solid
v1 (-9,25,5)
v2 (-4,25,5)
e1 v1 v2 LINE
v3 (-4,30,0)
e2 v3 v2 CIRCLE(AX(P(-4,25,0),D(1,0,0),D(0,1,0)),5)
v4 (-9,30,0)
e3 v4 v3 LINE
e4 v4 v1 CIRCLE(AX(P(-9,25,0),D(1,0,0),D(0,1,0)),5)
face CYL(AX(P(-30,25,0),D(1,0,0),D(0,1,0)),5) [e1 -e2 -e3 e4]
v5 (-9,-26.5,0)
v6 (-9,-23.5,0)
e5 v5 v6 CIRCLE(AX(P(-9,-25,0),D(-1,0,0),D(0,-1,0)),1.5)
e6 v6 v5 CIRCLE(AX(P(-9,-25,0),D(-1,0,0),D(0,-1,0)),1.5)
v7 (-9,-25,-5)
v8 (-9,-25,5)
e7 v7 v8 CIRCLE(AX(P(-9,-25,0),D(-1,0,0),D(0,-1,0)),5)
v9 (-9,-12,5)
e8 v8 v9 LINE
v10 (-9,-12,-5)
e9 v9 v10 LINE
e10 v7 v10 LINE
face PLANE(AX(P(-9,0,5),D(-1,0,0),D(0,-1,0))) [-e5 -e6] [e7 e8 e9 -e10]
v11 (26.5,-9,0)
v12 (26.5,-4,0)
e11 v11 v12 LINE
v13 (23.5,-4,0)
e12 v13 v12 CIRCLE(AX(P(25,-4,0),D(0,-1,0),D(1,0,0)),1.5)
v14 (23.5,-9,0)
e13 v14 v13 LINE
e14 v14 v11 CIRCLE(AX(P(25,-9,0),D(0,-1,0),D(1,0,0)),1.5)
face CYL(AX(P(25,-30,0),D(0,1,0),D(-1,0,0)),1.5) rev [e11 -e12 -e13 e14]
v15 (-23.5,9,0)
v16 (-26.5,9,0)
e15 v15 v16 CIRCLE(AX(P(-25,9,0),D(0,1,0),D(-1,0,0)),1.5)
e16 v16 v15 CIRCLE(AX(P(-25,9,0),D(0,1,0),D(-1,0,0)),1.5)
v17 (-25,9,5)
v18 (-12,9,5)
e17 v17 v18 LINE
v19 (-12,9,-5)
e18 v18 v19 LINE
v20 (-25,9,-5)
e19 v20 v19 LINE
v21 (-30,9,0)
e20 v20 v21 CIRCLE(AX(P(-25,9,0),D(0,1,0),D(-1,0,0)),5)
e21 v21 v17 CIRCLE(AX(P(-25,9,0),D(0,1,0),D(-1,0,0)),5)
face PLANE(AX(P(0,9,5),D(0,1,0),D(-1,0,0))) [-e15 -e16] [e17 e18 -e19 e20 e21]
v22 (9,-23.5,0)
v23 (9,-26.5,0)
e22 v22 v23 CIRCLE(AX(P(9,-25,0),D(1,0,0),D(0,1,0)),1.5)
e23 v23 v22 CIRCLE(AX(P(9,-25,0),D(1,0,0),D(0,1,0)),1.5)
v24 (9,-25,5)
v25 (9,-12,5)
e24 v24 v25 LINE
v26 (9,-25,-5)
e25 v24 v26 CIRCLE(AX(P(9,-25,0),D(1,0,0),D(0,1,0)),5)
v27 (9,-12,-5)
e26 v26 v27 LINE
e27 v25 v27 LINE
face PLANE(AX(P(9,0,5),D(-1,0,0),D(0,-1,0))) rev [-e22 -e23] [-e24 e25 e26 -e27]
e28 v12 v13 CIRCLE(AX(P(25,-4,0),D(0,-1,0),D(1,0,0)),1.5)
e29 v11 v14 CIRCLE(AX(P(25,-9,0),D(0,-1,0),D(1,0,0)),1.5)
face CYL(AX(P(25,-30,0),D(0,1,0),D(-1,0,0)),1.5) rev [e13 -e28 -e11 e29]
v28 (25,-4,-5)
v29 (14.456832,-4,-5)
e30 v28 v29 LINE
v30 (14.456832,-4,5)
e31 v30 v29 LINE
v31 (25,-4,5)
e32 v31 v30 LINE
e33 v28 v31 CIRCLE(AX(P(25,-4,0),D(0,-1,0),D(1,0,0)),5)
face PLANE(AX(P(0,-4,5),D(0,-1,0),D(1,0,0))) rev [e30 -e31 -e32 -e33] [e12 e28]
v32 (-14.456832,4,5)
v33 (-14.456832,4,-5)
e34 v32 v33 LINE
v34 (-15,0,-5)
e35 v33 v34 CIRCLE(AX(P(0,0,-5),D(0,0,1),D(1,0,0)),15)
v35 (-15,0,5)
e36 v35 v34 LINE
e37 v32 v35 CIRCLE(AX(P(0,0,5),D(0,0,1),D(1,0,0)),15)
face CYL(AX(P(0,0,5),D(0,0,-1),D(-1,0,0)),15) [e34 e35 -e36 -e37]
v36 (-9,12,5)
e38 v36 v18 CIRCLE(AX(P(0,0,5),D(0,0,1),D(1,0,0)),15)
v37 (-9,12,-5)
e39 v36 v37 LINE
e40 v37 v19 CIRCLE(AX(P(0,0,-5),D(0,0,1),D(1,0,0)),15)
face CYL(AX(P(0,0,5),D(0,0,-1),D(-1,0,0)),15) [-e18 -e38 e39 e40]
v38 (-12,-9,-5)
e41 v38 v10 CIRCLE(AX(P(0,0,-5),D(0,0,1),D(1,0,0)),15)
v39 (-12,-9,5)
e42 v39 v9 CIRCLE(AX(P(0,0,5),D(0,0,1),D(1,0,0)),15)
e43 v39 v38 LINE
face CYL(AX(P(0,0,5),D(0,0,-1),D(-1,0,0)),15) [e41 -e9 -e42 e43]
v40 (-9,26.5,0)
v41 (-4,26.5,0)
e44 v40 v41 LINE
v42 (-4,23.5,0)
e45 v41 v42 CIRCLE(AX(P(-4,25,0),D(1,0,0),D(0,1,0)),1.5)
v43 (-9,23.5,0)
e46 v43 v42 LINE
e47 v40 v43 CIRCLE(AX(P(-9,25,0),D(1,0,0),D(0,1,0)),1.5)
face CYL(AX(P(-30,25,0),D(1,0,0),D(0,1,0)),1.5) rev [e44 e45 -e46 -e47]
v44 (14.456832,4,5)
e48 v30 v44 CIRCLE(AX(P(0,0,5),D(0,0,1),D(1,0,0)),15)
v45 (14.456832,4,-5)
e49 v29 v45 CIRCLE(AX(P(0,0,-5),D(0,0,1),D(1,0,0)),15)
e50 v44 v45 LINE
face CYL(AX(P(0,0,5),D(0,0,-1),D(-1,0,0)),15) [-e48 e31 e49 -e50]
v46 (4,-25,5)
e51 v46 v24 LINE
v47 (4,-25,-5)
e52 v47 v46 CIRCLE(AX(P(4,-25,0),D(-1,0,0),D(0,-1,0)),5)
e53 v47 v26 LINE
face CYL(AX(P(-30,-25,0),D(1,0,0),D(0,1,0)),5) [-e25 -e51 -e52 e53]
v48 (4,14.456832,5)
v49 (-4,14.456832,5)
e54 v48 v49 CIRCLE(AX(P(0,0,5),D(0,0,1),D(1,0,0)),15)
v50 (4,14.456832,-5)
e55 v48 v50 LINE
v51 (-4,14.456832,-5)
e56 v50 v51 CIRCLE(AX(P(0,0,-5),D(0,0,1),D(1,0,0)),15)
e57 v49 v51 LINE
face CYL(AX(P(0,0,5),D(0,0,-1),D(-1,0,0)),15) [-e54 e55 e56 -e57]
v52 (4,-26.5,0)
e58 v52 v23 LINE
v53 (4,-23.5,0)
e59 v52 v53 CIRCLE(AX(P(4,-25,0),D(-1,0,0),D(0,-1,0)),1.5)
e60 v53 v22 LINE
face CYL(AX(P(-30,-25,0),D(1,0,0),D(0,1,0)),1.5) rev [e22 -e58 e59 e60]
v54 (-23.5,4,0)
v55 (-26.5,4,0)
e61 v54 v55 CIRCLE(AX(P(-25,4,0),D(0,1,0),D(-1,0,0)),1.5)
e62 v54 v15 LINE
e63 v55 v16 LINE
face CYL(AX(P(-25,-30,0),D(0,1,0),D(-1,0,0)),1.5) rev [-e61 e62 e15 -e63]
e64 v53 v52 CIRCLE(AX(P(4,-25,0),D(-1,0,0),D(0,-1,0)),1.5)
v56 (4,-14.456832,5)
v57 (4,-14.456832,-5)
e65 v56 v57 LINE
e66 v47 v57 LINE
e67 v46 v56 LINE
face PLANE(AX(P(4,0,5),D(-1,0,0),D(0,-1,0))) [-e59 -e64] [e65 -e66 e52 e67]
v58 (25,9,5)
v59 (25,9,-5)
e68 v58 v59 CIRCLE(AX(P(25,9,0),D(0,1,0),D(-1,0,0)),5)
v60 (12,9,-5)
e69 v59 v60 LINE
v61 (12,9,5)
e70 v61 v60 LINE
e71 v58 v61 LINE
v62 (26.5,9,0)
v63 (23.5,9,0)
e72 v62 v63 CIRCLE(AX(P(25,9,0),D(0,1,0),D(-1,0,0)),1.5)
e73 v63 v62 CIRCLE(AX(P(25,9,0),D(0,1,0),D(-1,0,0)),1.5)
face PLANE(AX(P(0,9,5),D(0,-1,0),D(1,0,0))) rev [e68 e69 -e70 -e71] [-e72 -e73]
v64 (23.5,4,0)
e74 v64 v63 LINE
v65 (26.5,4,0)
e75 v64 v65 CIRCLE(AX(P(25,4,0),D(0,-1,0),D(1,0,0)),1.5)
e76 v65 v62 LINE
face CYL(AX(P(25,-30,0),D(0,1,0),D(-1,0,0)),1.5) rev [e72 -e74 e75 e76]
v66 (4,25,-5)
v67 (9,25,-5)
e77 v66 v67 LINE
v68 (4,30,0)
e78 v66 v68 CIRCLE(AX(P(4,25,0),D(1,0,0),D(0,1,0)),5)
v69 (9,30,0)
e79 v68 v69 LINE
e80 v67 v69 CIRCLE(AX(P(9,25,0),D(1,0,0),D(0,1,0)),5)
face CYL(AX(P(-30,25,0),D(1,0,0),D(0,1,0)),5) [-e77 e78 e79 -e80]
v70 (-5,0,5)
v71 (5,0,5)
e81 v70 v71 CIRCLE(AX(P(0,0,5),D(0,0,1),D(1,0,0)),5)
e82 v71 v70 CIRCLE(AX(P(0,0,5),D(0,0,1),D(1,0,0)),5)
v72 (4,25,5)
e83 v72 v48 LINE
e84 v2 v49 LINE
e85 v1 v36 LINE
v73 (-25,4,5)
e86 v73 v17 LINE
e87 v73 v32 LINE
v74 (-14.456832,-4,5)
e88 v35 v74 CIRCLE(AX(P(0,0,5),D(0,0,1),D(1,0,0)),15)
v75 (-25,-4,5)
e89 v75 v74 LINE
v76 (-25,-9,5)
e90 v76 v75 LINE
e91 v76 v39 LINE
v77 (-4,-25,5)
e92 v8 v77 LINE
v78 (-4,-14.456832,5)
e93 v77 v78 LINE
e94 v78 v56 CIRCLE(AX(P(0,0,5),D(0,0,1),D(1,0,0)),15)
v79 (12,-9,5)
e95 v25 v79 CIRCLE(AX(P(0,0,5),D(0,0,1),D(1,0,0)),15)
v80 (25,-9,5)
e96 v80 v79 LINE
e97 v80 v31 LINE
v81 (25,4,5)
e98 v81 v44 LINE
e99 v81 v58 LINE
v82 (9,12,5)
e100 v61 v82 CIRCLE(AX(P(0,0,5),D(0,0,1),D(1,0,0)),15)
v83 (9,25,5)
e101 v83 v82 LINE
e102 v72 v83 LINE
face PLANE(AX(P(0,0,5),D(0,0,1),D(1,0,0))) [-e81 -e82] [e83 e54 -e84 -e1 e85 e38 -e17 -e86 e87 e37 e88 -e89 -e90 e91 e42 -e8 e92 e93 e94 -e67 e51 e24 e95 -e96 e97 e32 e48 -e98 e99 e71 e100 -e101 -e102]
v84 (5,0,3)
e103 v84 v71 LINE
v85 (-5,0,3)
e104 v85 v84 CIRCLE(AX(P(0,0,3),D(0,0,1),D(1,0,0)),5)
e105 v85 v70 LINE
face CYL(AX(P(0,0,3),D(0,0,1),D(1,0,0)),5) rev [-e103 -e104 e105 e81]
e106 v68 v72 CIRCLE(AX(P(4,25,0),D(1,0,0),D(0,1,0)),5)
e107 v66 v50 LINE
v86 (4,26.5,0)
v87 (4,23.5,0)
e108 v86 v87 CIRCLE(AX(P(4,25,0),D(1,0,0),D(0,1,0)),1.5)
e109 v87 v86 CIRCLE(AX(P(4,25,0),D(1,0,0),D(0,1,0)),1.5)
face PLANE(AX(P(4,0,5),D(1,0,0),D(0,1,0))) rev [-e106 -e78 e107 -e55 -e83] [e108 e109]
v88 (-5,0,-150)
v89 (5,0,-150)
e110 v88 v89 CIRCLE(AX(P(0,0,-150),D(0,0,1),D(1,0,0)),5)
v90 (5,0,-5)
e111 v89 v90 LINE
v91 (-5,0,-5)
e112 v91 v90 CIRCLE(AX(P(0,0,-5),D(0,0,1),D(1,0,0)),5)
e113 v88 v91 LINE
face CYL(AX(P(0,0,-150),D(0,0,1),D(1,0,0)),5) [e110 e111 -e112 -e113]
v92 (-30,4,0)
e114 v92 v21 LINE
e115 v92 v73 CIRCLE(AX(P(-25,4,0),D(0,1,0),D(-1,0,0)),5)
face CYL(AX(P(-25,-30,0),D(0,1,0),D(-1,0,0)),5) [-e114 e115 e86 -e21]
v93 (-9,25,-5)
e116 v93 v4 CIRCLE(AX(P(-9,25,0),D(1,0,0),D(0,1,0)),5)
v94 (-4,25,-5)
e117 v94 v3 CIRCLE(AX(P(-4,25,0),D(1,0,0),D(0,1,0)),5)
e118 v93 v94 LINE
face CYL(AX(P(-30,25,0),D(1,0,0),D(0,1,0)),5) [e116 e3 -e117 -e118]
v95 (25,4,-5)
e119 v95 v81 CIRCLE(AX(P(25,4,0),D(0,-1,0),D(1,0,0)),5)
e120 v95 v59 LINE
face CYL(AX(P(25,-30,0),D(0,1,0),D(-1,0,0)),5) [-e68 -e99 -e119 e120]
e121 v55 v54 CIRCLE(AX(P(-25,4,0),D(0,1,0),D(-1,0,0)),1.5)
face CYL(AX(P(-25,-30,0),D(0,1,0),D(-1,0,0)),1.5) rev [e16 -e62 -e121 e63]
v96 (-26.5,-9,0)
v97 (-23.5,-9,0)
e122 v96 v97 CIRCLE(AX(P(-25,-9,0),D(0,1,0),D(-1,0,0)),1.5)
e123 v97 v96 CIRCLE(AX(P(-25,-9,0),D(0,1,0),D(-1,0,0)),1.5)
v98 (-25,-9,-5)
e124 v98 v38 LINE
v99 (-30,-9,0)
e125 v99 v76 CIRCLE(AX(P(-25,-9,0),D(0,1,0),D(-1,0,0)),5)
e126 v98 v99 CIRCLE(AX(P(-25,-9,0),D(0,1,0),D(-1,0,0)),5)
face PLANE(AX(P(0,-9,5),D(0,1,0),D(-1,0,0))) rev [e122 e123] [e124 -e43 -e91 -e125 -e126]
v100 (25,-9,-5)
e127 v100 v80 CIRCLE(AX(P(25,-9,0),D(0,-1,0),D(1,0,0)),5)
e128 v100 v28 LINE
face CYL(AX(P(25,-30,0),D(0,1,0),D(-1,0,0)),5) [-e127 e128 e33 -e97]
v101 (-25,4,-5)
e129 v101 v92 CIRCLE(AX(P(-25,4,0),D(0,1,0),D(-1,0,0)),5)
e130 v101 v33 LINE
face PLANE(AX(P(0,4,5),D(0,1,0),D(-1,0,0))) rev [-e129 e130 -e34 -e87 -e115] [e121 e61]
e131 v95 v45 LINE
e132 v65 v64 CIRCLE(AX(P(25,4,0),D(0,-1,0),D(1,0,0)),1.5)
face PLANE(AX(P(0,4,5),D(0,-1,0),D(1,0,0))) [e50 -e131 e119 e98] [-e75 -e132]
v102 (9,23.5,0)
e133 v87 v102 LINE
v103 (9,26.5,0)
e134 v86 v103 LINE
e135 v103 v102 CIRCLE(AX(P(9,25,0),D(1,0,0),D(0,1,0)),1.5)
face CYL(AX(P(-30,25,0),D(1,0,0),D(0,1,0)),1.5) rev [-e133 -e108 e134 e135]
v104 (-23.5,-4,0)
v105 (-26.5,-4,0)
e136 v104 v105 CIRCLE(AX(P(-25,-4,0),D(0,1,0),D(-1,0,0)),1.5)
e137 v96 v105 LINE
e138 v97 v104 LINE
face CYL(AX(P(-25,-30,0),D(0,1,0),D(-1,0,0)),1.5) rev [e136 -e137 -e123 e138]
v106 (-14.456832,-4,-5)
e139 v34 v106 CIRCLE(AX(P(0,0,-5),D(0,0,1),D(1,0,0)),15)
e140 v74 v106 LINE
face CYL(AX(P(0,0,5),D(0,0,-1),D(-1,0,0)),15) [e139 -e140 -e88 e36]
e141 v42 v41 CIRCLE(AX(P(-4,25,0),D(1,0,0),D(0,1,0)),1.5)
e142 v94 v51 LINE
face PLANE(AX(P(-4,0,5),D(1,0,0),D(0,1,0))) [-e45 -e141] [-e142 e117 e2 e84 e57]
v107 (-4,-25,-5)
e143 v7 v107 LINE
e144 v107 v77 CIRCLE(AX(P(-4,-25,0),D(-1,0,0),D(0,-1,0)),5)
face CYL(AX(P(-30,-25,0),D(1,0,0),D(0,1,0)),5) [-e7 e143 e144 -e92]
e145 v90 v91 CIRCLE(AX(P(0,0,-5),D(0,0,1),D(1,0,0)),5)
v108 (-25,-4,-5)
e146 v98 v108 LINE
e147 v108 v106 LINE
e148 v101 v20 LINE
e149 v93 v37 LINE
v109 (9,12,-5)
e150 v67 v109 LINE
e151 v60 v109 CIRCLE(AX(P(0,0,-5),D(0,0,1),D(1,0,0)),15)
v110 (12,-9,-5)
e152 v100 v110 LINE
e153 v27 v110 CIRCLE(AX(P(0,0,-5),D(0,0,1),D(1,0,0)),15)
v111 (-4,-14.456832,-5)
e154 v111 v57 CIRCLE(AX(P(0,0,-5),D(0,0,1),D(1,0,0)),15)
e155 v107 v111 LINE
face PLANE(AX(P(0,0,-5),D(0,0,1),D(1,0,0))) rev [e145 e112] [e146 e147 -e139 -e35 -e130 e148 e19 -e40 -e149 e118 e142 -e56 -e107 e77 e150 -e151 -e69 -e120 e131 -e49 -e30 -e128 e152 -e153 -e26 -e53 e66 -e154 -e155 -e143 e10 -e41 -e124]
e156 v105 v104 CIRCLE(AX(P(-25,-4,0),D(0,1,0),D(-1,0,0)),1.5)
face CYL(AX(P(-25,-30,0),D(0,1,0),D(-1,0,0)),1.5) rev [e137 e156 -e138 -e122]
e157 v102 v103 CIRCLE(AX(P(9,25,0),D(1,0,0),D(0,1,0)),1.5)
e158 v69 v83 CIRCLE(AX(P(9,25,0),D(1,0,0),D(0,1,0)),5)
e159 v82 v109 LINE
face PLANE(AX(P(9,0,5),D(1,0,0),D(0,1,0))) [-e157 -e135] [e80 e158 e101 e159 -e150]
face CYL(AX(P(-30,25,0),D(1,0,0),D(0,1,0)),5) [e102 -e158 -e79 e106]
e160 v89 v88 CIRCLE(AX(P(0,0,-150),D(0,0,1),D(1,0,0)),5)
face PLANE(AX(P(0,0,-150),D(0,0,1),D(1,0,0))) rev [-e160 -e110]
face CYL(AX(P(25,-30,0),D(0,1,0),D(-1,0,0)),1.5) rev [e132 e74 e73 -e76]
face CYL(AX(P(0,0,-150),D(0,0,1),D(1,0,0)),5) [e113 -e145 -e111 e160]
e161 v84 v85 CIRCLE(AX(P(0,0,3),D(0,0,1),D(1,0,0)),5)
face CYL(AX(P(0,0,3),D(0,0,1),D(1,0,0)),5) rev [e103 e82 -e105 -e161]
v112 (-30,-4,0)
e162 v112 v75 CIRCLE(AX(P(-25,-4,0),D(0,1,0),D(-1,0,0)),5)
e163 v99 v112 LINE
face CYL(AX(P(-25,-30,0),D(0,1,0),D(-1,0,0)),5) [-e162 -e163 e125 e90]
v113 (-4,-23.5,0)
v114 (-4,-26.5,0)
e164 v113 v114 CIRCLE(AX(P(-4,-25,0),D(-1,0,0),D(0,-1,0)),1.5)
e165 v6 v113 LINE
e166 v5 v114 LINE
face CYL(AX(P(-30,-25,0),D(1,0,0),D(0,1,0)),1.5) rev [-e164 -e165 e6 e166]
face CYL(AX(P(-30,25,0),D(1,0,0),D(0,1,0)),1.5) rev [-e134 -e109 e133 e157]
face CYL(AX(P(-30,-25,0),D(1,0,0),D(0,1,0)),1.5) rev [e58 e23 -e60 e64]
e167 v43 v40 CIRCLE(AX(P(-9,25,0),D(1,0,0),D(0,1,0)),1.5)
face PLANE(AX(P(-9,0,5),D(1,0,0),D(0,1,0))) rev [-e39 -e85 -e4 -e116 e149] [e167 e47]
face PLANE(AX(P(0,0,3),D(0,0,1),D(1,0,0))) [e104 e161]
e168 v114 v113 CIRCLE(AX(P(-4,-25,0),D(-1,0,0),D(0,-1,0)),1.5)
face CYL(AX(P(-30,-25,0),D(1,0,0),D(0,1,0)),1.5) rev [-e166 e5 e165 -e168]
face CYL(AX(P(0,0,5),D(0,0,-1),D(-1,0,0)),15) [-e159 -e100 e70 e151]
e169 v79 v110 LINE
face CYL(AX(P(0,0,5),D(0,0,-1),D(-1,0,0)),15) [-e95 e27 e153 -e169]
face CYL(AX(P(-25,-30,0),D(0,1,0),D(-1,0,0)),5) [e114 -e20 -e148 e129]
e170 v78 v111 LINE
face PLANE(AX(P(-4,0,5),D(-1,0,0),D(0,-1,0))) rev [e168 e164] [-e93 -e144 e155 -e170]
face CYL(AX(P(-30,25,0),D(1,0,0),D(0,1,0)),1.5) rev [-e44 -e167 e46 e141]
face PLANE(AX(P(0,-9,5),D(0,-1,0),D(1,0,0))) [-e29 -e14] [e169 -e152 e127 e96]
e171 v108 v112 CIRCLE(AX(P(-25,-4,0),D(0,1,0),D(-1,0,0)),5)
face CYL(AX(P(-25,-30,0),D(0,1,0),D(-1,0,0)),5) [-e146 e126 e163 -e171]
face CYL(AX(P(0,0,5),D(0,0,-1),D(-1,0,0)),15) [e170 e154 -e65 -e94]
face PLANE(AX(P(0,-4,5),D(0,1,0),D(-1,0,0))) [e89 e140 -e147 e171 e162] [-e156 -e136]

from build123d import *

# Parameters (mm, degrees)
CROSS_FLANGE_DEPTH        = 5
SKETCH1_3_R               = 5
SHAFT_150_DEPTH           = 150
ARM_HOLES_A_SKETCH_R      = 1.5
ARM_HOLES_A_DEPTH         = 158.863865403
ARM_HOLES_B_SKETCH_R      = 1.5
ARM_HOLES_B_DEPTH         = 158.863865403
CENTER_RECESS_10_SKETCH_R = 5
CENTER_RECESS_10_X2_DEPTH = 2


with BuildPart() as part:
    # Cross Flange Profile → Cross Flange (new, symmetric)
    with BuildSketch(Plane.XY):
        with BuildLine():
            Line((-4, 14.456832295), (-4, 30))
            Line((-4, 30), (-9, 30))
            Line((-9, 30), (-9, 12))
            ThreePointArc((-9, 12), (-10.606601718, 10.606601718), (-12, 9))
            Line((-12, 9), (-30, 9))
            Line((-30, 9), (-30, 4))
            Line((-30, 4), (-14.456832295, 4))
            ThreePointArc((-14.456832295, 4), (-15, 0), (-14.456832295, -4))
            Line((-14.456832295, -4), (-30, -4))
            Line((-30, -4), (-30, -9))
            Line((-30, -9), (-12, -9))
            ThreePointArc((-12, -9), (-10.606601718, -10.606601718), (-9, -12))
            Line((-9, -12), (-9, -30))
            Line((-9, -30), (-4, -30))
            Line((-4, -30), (-4, -14.456832295))
            ThreePointArc((-4, -14.456832295), (0, -15), (4, -14.456832295))
            Line((4, -14.456832295), (4, -30))
            Line((4, -30), (9, -30))
            Line((9, -30), (9, -12))
            ThreePointArc((9, -12), (10.606601718, -10.606601718), (12, -9))
            Line((12, -9), (30, -9))
            Line((30, -9), (30, -4))
            Line((30, -4), (14.456832295, -4))
            ThreePointArc((14.456832295, -4), (15, 0), (14.456832295, 4))
            Line((14.456832295, 4), (30, 4))
            Line((30, 4), (30, 9))
            Line((30, 9), (12, 9))
            ThreePointArc((12, 9), (10.606601718, 10.606601718), (9, 12))
            Line((9, 12), (9, 30))
            Line((9, 30), (4, 30))
            Line((4, 30), (4, 14.456832295))
            ThreePointArc((4, 14.456832295), (0, 15), (-4, 14.456832295))
        make_face()
    extrude(amount=CROSS_FLANGE_DEPTH, both=True)

    # Sketch1_3 → Shaft 150 (add)
    with BuildSketch(Plane.XY):
        Circle(SKETCH1_3_R)
    extrude(amount=-SHAFT_150_DEPTH)

    # Arm Holes A Sketch → Arm Holes A (cut, through all)
    with BuildSketch(Plane(origin=(9, 0, 0), x_dir=(0, 0, -1), z_dir=(1, 0, 0))):
        with BuildLine():
            ThreePointArc((0, -30), (-3.535533906, -28.535533906), (-5, -25))
            Line((-5, -25), (-5, -30))
            Line((-5, -30), (0, -30))
        make_face()
        with BuildLine():
            ThreePointArc((5, -25), (3.535533906, -28.535533906), (0, -30))
            Line((0, -30), (5, -30))
            Line((5, -30), (5, -25))
        make_face()
        with BuildLine():
            Line((-5, 30), (-5, 25))
            ThreePointArc((-5, 25), (-3.535533906, 28.535533906), (0, 30))
            Line((0, 30), (-5, 30))
        make_face()
        with BuildLine():
            Line((5, 30), (0, 30))
            ThreePointArc((0, 30), (3.535533906, 28.535533906), (5, 25))
            Line((5, 25), (5, 30))
        make_face()
        with Locations(Location((0, 25, 0), (0, 0, 90))):
            Circle(ARM_HOLES_A_SKETCH_R)
        with Locations(Location((0, -25, 0), (0, 0, 90))):
            Circle(ARM_HOLES_A_SKETCH_R)
    extrude(amount=-ARM_HOLES_A_DEPTH, mode=Mode.SUBTRACT)

    # Arm Holes B Sketch → Arm Holes B (cut, through all)
    with BuildSketch(Plane(origin=(0, 9, 0), x_dir=(1, 0, 0), z_dir=(0, 1, 0))):
        with BuildLine():
            ThreePointArc((30, 0), (28.535533906, -3.535533906), (25, -5))
            Line((25, -5), (30, -5))
            Line((30, -5), (30, 0))
        make_face()
        with BuildLine():
            ThreePointArc((25, 5), (28.535533906, 3.535533906), (30, 0))
            Line((30, 0), (30, 5))
            Line((30, 5), (25, 5))
        make_face()
        with BuildLine():
            Line((-30, -5), (-25, -5))
            ThreePointArc((-25, -5), (-28.535533906, -3.535533906), (-30, 0))
            Line((-30, 0), (-30, -5))
        make_face()
        with BuildLine():
            Line((-30, 5), (-30, 0))
            ThreePointArc((-30, 0), (-28.535533906, 3.535533906), (-25, 5))
            Line((-25, 5), (-30, 5))
        make_face()
        with Locations(Location((-25, 0, 0), (0, 0, 180))):
            Circle(ARM_HOLES_B_SKETCH_R)
        with Locations((25, 0)):
            Circle(ARM_HOLES_B_SKETCH_R)
    extrude(amount=-ARM_HOLES_B_DEPTH, mode=Mode.SUBTRACT)

    # Center Recess _10 Sketch → Center Recess _10 x2 (cut)
    with BuildSketch(Plane.XY.offset(5)):
        Circle(CENTER_RECESS_10_SKETCH_R)
    extrude(amount=-CENTER_RECESS_10_X2_DEPTH, mode=Mode.SUBTRACT)


solid = part.part
